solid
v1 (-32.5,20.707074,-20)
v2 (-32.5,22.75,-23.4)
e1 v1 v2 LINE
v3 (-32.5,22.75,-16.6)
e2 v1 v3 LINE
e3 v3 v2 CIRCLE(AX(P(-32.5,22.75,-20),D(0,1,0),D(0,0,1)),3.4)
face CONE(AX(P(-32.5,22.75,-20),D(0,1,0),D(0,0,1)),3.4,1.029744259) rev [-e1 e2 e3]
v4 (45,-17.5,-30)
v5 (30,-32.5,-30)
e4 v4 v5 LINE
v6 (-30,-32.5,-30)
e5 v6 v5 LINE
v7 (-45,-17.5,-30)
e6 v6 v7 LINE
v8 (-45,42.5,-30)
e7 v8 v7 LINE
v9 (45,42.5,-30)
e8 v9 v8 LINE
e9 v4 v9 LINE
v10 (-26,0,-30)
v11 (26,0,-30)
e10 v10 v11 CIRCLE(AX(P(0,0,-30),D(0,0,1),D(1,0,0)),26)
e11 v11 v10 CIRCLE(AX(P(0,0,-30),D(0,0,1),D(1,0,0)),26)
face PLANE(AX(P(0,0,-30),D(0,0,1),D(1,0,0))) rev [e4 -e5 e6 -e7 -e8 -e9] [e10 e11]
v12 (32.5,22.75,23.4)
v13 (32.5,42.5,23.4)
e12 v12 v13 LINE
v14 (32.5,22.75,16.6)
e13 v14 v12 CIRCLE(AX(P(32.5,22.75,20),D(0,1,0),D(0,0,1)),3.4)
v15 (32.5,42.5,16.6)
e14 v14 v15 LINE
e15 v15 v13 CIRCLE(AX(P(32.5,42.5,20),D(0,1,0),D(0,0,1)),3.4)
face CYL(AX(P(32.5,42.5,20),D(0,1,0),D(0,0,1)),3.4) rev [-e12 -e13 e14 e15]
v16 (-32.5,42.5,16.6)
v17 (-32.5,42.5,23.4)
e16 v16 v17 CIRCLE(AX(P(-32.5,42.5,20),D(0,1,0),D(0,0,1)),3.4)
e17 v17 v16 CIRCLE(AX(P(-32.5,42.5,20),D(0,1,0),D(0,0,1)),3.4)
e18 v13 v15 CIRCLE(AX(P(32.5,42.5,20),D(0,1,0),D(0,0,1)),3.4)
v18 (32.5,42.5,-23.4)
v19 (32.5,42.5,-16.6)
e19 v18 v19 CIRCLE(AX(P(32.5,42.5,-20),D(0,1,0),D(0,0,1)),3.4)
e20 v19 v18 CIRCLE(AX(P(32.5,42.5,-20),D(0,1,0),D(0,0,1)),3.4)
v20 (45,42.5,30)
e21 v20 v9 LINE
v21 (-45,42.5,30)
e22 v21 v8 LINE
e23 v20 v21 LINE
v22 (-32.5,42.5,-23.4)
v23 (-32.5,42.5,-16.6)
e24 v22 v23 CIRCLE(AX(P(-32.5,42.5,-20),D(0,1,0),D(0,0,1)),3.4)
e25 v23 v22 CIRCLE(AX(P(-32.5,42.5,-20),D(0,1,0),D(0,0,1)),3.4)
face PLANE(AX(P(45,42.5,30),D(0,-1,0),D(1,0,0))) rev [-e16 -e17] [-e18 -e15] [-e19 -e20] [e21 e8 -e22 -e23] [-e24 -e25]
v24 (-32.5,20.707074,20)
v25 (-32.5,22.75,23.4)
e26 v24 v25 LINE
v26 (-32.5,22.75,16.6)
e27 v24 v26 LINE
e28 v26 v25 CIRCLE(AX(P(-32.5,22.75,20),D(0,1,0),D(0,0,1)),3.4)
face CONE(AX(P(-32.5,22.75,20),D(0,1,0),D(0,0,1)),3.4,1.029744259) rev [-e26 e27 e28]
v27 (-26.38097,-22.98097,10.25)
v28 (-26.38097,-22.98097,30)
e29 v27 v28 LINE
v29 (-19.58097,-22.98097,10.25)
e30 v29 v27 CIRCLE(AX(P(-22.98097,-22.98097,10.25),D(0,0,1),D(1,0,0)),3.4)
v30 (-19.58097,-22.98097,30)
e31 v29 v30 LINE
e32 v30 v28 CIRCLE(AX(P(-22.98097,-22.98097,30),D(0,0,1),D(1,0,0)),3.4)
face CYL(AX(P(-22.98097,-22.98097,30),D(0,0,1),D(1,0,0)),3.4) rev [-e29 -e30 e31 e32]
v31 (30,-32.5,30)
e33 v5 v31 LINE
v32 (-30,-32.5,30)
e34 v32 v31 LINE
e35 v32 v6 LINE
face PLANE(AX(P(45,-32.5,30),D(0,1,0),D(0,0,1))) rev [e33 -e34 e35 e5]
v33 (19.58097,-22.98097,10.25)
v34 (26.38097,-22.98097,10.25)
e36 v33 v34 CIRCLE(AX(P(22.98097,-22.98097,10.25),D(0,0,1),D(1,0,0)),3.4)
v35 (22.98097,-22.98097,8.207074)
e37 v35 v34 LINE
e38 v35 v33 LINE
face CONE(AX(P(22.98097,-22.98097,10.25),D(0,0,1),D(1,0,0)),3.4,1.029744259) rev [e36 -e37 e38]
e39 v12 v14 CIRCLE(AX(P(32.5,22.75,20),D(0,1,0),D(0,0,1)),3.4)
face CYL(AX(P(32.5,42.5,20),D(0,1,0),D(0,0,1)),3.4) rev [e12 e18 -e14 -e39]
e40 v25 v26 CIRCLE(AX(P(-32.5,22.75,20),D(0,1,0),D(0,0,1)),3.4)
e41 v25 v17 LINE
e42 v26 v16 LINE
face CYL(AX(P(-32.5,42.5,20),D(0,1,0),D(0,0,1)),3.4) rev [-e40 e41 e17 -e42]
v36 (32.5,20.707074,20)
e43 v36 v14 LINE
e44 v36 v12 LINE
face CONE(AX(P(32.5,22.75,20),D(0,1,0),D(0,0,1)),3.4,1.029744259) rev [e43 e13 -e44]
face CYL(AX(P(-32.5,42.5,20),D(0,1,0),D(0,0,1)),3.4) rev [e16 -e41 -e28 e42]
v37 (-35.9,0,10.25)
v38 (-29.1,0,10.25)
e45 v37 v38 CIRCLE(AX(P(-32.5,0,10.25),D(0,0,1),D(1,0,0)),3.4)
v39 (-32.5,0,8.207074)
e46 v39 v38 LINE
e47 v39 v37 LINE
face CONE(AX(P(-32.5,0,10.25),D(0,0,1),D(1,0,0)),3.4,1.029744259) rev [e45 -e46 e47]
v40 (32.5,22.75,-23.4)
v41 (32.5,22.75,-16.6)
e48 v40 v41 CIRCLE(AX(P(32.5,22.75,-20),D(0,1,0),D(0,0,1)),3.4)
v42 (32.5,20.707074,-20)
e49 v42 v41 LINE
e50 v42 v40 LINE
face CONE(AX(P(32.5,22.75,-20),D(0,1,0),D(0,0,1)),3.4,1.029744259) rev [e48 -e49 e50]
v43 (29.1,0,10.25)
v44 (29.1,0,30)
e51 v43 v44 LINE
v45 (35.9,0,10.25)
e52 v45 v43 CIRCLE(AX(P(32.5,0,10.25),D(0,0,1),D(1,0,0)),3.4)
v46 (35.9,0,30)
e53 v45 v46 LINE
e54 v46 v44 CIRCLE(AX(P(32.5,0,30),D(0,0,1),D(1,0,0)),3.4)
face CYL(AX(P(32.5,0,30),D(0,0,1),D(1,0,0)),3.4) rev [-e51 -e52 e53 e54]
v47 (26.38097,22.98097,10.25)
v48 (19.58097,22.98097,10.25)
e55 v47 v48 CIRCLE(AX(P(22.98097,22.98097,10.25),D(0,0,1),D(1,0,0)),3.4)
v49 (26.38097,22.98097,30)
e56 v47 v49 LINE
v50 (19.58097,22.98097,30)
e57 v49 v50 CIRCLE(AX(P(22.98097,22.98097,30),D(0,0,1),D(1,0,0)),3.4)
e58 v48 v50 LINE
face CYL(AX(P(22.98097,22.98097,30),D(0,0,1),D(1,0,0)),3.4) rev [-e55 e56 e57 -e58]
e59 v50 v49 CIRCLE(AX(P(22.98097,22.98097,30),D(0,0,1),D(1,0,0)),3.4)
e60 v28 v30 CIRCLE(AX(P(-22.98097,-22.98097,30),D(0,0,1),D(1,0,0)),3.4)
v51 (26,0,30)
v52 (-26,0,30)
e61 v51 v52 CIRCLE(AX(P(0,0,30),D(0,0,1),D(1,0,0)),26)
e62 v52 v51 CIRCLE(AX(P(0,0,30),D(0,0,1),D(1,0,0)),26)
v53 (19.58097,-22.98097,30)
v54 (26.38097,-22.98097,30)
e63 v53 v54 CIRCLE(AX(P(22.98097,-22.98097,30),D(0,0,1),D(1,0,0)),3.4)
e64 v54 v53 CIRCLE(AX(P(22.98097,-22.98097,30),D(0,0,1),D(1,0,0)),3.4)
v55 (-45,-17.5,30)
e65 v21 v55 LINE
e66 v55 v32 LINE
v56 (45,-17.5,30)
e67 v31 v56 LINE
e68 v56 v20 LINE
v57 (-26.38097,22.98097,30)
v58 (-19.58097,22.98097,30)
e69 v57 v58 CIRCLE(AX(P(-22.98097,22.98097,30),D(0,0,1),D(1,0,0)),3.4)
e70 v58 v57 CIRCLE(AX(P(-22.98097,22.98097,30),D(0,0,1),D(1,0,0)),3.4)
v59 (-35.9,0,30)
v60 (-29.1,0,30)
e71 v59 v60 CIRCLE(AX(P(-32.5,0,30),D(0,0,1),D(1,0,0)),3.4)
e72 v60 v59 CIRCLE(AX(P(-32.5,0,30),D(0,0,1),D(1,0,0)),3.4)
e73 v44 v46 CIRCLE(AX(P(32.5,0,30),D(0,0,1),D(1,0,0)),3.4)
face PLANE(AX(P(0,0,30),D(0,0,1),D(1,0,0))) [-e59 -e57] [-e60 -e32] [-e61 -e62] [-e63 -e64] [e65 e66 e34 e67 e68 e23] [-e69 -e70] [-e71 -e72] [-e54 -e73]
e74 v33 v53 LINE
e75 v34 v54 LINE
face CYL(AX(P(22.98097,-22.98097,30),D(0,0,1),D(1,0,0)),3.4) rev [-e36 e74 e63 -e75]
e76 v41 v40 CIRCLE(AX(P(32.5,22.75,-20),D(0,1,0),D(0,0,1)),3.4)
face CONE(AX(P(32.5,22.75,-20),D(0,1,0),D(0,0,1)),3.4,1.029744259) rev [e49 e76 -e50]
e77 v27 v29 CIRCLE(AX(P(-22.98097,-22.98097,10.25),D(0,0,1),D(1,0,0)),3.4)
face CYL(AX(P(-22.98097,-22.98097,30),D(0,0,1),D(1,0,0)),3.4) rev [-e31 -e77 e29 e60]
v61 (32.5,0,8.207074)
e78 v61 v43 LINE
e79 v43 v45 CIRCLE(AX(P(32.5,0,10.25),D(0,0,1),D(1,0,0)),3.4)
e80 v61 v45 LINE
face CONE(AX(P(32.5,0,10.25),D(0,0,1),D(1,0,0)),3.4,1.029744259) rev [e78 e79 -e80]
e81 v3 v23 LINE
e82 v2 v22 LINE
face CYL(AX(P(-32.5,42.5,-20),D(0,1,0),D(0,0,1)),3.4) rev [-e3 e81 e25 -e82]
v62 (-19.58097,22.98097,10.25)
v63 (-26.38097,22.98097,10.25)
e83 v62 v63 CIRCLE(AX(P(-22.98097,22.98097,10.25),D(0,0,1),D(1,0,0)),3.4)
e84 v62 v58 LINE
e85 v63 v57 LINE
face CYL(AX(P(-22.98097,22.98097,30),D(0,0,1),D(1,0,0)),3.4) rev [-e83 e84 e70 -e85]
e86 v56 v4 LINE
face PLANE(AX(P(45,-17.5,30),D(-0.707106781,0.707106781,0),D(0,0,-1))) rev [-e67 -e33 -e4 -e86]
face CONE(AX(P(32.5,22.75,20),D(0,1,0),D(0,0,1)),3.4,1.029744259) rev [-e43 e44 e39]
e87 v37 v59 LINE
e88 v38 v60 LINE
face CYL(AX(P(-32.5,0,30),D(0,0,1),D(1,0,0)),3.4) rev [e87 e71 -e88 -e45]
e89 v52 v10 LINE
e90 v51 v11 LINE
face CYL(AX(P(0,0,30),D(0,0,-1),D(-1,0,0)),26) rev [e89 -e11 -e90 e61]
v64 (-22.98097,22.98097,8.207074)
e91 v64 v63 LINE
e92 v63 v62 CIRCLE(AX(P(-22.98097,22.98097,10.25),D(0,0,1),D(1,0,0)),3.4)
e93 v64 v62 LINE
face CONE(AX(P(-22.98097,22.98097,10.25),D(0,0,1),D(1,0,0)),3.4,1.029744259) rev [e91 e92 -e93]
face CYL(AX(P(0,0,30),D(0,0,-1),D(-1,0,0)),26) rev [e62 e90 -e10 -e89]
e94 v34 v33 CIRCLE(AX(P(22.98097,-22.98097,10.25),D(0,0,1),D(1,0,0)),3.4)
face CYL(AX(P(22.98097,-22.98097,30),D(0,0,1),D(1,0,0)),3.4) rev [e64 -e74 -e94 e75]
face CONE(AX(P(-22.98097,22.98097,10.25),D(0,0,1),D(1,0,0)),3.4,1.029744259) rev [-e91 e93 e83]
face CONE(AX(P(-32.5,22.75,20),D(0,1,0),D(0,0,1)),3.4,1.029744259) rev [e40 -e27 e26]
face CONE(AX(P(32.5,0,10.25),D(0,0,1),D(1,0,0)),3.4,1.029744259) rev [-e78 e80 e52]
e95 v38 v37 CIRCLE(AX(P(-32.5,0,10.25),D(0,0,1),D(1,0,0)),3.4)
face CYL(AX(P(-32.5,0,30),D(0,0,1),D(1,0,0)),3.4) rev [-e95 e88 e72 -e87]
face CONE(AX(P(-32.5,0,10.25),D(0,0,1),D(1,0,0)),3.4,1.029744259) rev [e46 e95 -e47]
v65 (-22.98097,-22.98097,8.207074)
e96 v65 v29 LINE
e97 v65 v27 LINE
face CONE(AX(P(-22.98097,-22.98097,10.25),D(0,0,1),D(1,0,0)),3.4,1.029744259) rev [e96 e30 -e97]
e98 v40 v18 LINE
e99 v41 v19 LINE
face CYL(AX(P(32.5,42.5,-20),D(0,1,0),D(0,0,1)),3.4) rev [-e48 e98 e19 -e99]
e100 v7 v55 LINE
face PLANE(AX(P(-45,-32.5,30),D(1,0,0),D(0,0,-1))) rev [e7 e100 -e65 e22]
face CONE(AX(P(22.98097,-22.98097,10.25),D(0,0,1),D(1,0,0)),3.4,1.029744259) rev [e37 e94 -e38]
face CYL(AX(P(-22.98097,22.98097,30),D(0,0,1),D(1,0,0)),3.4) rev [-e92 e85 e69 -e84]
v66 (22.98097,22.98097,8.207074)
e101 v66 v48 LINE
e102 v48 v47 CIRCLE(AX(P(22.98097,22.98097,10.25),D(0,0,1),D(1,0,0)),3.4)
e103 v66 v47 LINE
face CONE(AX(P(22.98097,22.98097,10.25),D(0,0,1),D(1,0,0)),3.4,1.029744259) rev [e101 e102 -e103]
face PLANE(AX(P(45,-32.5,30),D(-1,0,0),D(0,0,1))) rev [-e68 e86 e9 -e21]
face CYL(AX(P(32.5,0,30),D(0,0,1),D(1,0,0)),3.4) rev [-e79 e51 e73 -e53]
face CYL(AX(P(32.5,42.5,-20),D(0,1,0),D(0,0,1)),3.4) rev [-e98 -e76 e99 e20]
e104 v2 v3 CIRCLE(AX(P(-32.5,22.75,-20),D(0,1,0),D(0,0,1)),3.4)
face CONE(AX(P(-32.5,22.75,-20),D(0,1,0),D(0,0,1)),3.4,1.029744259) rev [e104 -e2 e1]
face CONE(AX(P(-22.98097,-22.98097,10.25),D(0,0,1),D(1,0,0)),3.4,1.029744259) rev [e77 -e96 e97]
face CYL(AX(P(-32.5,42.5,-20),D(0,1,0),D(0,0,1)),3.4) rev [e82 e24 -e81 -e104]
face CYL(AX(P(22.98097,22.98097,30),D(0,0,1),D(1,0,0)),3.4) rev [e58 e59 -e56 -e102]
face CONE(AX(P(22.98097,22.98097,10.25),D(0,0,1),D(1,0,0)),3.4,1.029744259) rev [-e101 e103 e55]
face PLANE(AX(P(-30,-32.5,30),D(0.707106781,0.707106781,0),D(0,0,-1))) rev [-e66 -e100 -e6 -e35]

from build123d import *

# Parameters (mm, degrees)
SKETCH_1_W             = 90
SKETCH_1_H             = 75
SKETCH_1_R             = 26
EXTRUDE_1_DEPTH        = 30
HOLE_WIZARD_M8_1_D     = 6.8
HOLE_WIZARD_M8_1_DEPTH = 19.75
HOLE_WIZARD_M8_1_TIP   = 2.042926105
CHAMFER_1_SIZE         = 15
HOLE_WIZARD_M8_2_D     = 6.8
HOLE_WIZARD_M8_2_DEPTH = 19.75
HOLE_WIZARD_M8_2_TIP   = 2.042926105


with BuildPart() as part:
    # 草图1 → 凸台-拉伸1 (new, symmetric)
    with BuildSketch(Plane.XY):
        with Locations((0, 5)):
            Rectangle(SKETCH_1_W, SKETCH_1_H)
        Circle(SKETCH_1_R, mode=Mode.SUBTRACT)
    extrude(amount=EXTRUDE_1_DEPTH, both=True)

    # M8 螺纹孔1
    with Locations(Plane(origin=(-32.5, 0, 30), x_dir=(1, 0, 0), z_dir=(0, 0, 1))):
        with Locations((0, 0), (9.519029611, 22.980970389), (9.519029611, -22.980970389), (55.480970389, -22.980970389), (65, 0), (55.480970389, 22.980970389)):
            Hole(HOLE_WIZARD_M8_1_D / 2, depth=HOLE_WIZARD_M8_1_DEPTH)
            with Locations((0, 0, -(HOLE_WIZARD_M8_1_DEPTH + HOLE_WIZARD_M8_1_TIP / 2))):  # 118° drill point
                Cone(0, HOLE_WIZARD_M8_1_D / 2, HOLE_WIZARD_M8_1_TIP, mode=Mode.SUBTRACT)

    # 倒角1
    chamfer_1_edges = [part.edges().sort_by_distance(p)[0] for p in [
        (45, -32.5, 0),
        (-45, -32.5, 0),
    ]]
    chamfer(chamfer_1_edges, length=CHAMFER_1_SIZE)

    # M8 螺纹孔2
    with Locations(Plane(origin=(32.5, 42.5, -20), x_dir=(1, 0, 0), z_dir=(0, 1, 0))):
        with Locations((0, 0), (0, -40), (-65, -40), (-65, 0)):
            Hole(HOLE_WIZARD_M8_2_D / 2, depth=HOLE_WIZARD_M8_2_DEPTH)
            with Locations((0, 0, -(HOLE_WIZARD_M8_2_DEPTH + HOLE_WIZARD_M8_2_TIP / 2))):  # 118° drill point
                Cone(0, HOLE_WIZARD_M8_2_D / 2, HOLE_WIZARD_M8_2_TIP, mode=Mode.SUBTRACT)


solid = part.part
